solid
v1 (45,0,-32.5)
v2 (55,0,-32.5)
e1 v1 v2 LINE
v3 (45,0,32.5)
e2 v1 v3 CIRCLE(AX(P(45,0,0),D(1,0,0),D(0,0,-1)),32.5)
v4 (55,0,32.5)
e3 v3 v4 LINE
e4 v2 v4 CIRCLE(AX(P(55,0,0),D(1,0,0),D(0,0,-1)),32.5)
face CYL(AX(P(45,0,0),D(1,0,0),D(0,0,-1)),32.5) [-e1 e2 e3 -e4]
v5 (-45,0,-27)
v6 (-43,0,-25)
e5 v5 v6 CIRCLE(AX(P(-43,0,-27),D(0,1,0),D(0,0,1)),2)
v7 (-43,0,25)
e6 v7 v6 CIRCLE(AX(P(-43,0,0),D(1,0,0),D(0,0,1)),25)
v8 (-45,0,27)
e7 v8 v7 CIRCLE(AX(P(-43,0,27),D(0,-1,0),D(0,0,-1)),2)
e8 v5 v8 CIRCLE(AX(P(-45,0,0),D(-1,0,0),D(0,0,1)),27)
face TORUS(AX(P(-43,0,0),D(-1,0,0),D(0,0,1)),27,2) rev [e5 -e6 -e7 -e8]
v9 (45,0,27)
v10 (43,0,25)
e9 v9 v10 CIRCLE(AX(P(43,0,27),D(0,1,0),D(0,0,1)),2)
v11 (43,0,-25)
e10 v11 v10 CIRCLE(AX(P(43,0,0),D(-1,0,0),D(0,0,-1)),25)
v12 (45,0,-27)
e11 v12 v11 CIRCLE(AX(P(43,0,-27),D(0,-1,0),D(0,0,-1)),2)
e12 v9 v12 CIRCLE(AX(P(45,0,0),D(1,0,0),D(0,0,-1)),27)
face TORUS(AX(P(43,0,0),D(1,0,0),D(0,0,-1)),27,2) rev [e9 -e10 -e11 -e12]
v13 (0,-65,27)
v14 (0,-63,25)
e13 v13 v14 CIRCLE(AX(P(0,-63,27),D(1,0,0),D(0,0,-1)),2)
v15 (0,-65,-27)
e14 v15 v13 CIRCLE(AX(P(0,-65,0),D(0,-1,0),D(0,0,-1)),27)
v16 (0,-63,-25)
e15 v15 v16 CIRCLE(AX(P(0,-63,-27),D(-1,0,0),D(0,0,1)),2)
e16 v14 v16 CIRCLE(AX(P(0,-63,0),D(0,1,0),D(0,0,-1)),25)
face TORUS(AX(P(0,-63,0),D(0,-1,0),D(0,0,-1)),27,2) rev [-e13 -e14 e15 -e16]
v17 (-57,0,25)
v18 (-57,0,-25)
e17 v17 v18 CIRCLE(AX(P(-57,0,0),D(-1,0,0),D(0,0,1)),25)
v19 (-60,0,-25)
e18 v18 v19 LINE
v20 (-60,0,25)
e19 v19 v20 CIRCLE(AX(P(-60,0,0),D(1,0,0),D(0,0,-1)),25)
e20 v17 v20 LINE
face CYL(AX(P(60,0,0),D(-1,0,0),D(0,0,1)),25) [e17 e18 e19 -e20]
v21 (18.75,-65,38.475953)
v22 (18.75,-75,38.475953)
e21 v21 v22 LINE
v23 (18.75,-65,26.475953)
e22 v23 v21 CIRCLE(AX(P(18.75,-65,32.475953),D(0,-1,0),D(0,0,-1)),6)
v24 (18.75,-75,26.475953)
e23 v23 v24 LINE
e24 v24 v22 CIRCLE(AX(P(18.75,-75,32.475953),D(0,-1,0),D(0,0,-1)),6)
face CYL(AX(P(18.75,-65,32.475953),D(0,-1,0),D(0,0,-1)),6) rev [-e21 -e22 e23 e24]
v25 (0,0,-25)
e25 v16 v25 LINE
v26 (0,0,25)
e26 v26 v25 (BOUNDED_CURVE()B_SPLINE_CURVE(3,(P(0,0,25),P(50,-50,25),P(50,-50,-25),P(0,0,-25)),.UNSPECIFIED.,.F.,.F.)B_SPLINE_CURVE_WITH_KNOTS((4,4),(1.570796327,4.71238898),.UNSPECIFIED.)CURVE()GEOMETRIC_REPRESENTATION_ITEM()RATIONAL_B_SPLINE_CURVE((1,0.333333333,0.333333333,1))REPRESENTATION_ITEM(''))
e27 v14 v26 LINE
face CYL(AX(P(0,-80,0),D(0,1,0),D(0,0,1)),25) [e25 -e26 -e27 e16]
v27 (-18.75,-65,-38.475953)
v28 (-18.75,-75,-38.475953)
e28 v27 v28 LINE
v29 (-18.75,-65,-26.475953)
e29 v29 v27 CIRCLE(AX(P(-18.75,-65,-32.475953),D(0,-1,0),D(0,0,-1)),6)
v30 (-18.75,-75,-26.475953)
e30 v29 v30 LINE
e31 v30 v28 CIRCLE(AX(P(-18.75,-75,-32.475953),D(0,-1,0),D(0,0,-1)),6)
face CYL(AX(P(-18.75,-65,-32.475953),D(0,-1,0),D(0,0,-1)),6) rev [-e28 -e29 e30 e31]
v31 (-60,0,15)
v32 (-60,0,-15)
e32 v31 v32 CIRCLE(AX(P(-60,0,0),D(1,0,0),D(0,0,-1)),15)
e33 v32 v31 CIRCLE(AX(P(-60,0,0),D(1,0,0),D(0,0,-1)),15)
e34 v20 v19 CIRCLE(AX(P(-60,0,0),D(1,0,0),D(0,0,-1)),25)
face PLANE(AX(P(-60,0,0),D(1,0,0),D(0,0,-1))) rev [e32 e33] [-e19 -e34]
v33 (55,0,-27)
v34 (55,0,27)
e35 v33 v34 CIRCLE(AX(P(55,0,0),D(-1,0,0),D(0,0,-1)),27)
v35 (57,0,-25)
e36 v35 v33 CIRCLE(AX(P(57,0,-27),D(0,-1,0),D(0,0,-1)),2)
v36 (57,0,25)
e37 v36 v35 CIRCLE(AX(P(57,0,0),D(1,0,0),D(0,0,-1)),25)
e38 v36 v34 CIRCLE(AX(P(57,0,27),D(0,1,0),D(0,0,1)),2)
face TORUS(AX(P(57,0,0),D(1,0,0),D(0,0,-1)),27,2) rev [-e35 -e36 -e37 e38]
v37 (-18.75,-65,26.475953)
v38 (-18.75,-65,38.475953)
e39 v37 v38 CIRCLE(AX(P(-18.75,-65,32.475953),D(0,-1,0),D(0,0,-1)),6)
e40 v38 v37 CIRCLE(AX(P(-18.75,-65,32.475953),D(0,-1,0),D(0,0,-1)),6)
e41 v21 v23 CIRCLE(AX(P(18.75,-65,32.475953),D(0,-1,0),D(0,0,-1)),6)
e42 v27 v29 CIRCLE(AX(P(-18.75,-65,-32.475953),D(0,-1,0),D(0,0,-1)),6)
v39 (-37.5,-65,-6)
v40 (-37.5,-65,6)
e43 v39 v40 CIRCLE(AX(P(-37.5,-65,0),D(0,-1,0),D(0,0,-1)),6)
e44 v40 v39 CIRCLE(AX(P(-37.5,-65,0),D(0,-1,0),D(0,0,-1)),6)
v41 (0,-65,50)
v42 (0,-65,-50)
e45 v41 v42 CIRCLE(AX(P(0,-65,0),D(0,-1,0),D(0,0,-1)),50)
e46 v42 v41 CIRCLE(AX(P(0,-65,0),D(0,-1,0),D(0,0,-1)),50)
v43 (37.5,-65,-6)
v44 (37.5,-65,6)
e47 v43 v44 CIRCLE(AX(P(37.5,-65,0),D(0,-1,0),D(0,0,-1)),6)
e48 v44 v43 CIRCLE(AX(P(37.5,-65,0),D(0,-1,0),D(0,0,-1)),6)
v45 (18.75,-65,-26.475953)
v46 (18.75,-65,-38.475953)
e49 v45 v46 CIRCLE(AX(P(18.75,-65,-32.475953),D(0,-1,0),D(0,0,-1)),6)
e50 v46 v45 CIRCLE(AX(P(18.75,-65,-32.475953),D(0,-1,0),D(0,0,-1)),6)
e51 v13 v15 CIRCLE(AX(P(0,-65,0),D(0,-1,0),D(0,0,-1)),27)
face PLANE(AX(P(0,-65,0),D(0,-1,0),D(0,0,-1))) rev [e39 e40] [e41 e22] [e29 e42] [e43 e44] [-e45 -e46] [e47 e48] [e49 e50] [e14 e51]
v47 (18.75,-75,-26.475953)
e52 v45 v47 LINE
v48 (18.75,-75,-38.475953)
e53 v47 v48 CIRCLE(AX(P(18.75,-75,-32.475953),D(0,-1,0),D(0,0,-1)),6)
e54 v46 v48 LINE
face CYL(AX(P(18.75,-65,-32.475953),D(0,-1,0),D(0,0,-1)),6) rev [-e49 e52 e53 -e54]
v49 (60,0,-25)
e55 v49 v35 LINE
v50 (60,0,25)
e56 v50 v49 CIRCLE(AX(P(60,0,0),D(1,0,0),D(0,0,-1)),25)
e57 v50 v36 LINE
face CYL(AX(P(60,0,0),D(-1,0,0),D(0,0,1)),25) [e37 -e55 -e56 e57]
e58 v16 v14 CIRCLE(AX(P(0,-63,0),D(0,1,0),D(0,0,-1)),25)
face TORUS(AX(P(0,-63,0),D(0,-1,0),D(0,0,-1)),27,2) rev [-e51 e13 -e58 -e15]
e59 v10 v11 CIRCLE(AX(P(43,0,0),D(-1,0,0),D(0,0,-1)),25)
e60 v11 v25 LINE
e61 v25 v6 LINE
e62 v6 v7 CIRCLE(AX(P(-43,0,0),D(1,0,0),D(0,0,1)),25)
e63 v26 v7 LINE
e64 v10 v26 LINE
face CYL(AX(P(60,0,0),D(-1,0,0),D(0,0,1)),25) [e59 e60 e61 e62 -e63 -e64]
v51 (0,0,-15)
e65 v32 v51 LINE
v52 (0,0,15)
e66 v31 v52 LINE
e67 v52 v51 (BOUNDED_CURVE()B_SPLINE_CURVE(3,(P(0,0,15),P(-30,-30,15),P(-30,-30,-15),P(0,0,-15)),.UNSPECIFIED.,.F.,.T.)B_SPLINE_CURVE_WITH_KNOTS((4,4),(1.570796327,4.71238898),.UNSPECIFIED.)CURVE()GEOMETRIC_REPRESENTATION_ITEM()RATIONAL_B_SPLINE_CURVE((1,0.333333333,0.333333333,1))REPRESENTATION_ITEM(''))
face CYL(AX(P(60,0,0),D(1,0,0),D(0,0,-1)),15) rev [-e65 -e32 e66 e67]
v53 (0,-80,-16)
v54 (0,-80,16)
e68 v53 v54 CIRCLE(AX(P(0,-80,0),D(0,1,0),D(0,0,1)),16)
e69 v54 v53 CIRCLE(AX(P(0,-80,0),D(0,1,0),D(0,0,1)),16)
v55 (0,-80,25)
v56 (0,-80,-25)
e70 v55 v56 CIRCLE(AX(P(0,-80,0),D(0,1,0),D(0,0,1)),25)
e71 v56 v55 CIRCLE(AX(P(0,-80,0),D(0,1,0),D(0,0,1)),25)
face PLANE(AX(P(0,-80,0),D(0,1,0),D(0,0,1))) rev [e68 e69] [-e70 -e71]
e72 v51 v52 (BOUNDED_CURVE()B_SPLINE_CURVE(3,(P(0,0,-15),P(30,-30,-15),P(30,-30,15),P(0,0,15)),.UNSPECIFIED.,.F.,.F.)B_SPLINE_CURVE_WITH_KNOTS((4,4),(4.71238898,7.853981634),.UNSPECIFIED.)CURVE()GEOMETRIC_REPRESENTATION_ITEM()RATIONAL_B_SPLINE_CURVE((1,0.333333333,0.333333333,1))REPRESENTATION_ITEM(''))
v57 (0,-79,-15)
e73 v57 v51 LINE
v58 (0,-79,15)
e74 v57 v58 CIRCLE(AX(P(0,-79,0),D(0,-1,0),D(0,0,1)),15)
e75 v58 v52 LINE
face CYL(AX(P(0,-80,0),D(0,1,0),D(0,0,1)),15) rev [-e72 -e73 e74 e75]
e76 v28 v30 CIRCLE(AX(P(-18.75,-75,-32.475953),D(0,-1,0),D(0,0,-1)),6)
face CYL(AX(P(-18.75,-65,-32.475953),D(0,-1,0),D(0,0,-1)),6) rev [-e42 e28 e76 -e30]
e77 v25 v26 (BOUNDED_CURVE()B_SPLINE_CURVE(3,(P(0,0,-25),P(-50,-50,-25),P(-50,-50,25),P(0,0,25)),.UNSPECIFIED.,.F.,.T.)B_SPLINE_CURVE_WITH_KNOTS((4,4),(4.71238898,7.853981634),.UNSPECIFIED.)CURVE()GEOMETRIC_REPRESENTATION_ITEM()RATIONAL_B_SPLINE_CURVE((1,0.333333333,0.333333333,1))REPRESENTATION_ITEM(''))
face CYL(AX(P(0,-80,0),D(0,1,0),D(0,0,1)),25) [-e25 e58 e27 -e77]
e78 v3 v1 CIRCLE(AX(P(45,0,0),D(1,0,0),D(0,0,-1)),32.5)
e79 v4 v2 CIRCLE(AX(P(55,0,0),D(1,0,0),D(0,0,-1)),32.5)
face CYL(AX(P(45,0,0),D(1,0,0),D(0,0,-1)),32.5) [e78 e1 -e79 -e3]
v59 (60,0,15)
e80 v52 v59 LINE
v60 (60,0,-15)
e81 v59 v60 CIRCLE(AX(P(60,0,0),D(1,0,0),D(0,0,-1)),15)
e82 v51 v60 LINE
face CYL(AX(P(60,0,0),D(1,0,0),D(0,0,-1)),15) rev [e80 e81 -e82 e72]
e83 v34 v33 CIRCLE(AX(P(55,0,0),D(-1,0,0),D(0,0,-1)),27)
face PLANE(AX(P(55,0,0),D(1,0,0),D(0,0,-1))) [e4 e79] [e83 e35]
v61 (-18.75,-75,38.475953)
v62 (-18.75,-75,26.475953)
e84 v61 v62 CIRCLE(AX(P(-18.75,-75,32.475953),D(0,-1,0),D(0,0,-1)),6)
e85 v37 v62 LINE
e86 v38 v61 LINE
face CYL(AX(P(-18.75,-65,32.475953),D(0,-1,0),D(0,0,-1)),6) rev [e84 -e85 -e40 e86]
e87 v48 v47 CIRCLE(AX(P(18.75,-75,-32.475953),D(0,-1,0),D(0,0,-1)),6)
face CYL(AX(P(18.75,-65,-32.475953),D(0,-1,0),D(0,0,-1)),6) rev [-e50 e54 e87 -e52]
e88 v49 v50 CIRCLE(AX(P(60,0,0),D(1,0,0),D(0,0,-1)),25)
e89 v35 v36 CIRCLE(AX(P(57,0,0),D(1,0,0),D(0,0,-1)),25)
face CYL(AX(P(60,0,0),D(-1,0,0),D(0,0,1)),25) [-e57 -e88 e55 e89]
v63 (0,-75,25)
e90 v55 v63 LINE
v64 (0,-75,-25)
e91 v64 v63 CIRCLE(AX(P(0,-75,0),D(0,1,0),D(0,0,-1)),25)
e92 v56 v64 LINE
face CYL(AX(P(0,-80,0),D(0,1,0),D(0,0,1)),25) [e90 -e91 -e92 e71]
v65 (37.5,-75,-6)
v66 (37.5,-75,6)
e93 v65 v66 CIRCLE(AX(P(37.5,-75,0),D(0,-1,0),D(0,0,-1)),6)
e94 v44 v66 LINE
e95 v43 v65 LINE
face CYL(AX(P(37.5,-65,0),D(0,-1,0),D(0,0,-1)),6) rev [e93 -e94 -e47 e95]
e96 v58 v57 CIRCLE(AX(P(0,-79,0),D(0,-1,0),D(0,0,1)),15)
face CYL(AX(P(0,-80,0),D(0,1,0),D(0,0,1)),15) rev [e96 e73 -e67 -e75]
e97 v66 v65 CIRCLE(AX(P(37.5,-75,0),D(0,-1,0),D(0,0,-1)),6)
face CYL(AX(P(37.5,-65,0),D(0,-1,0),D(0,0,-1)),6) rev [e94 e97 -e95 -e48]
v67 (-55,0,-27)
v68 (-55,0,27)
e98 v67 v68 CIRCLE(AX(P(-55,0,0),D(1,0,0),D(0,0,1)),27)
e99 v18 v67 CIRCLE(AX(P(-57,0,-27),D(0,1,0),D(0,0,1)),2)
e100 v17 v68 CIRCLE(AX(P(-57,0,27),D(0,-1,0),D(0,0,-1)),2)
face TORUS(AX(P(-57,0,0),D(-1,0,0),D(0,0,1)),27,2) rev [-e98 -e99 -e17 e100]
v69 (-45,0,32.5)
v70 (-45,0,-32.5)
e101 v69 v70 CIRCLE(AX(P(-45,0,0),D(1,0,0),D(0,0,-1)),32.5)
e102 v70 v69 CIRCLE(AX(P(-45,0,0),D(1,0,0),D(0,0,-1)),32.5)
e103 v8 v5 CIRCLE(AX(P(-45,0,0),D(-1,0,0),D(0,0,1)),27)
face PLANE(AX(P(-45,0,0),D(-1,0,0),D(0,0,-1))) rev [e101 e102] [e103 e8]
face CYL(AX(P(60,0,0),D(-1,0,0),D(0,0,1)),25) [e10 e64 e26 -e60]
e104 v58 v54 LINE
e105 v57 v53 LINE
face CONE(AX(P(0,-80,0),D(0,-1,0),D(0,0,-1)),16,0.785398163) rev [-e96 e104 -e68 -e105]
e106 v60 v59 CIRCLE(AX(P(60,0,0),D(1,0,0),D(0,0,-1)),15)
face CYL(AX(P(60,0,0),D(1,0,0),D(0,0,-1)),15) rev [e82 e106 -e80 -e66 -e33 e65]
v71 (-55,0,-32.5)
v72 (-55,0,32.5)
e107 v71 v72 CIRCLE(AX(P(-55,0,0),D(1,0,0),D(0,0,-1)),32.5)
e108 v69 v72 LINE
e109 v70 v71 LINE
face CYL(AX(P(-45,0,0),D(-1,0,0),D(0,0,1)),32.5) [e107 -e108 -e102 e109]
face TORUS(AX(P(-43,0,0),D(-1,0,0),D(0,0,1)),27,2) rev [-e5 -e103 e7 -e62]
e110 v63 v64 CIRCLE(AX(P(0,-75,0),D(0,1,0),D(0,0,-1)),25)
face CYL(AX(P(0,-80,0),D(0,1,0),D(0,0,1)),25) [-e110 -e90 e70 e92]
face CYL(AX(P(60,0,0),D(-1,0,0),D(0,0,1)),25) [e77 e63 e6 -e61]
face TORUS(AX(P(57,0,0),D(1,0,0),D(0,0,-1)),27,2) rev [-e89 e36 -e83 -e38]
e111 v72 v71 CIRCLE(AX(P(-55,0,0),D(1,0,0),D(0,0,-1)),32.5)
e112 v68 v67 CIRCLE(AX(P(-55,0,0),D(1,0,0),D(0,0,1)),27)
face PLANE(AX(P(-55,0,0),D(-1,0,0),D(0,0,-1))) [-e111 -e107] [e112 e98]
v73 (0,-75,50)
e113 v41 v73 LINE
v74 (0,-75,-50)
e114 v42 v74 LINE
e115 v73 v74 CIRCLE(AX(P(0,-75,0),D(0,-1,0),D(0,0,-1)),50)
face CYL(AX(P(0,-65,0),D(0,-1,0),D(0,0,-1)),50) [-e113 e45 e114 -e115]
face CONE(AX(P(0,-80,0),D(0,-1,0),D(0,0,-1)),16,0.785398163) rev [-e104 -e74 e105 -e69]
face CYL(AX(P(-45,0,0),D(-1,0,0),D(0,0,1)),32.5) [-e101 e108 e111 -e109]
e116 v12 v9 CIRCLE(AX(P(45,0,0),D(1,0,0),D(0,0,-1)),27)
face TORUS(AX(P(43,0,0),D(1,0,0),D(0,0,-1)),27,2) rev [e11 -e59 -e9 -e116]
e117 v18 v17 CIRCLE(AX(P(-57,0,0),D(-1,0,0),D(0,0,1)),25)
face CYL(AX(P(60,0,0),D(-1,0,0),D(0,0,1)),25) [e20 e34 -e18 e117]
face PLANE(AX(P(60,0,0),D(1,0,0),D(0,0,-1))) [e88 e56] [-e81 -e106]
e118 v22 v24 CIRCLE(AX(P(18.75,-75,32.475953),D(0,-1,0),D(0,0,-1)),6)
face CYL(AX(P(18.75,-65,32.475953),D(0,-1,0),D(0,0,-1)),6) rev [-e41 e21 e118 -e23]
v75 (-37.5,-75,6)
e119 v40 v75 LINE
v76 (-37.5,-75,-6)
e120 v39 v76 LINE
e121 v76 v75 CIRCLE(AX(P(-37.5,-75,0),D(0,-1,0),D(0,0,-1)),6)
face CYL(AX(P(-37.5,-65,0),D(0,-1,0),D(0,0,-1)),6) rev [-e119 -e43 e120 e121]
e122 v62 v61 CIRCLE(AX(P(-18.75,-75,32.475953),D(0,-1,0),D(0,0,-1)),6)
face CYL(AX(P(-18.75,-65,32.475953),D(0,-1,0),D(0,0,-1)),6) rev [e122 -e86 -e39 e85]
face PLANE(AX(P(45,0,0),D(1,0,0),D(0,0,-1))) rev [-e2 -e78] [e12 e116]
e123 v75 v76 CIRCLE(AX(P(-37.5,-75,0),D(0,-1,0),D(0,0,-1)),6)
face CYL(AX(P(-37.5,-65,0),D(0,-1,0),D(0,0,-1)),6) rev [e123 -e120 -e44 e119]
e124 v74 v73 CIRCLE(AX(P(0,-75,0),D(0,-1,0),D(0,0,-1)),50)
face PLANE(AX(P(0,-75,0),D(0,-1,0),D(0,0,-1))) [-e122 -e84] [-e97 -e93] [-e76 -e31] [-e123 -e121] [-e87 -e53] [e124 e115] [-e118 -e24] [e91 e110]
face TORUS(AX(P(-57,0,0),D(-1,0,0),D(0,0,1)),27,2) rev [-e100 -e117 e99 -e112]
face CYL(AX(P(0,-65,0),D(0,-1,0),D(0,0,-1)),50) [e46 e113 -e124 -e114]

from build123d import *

# Parameters (mm, degrees)
MAIN_PIPE_SKETCH_R             = 25
MAIN_PIPE_50X120_DEPTH         = 60
END_START                      = -5
END_COLLAR_SKETCH_R            = 32.5
END_COLLAR_SKETCH_R_2          = 25
END_COLLAR_65_DEPTH            = 10
BRANCH_PIPE_SKETCH_R           = 25
BRANCH_PIPE_SKETCH_R_2         = 15
BRANCH_PIPE_50_DEPTH           = 80
MAIN_BORE_30_THRU_D            = 30
BRANCH_BORE_SKETCH_R           = 15
BRANCH_BORE_CUT_DEPTH          = 80
BASE_START                     = -15
BASE_FLANGE_SKETCH_R           = 50
BASE_FLANGE_SKETCH_R_2         = 6
BASE_FLANGE_SKETCH_R_3         = 25
BASE_FLANGE_100_6X_12_DEPTH    = 10
COLLAR_AND_FLANGE_FILLETS_R2_R = 2
BRANCH_EDGE_CHAMFER_1MM_SIZE   = 1


with BuildPart() as part:
    # Main Pipe Sketch → Main Pipe Ø50x120 (new, symmetric)
    with BuildSketch(Plane(origin=(0, 0, 0), x_dir=(0, 0, -1), z_dir=(1, 0, 0))):
        Circle(MAIN_PIPE_SKETCH_R)
    extrude(amount=MAIN_PIPE_50X120_DEPTH, both=True)

    # End Collar Sketch → End Collar Ø65 (add)
    with BuildSketch(Plane(origin=(60, 0, 0), x_dir=(0, 0, -1), z_dir=(1, 0, 0)).offset(END_START)):
        Circle(END_COLLAR_SKETCH_R)
        Circle(END_COLLAR_SKETCH_R_2, mode=Mode.SUBTRACT)
    end_collar_65 = extrude(amount=-END_COLLAR_65_DEPTH)

    # End Collar Mirror: End Collar Ø65 across plane
    add(end_collar_65.mirror(Plane(origin=(0, 0, 0), x_dir=(0, 0, 1), z_dir=(1, 0, 0))))

    # Branch Pipe Sketch → Branch Pipe Ø50 (add)
    with BuildSketch(Plane(origin=(0, 0, 0), x_dir=(1, 0, 0), z_dir=(0, 1, 0))):
        with Locations(Location((0, 0, 0), (0, 0, 270))):
            Circle(BRANCH_PIPE_SKETCH_R)
        with Locations(Location((0, 0, 0), (0, 0, 270))):
            Circle(BRANCH_PIPE_SKETCH_R_2, mode=Mode.SUBTRACT)
    extrude(amount=-BRANCH_PIPE_50_DEPTH)

    # Main Bore Ø30 Thru (through all)
    with Locations(Plane(origin=(60, 0, 0), x_dir=(0, 0, -1), z_dir=(1, 0, 0))):
        with Locations((0, 0)):
            Hole(MAIN_BORE_30_THRU_D / 2)

    # Branch Bore Sketch → Branch Bore Cut (cut)
    with BuildSketch(Plane(origin=(0, 0, 0), x_dir=(1, 0, 0), z_dir=(0, 1, 0))):
        with Locations(Location((0, 0, 0), (0, 0, 270))):
            Circle(BRANCH_BORE_SKETCH_R)
    extrude(amount=-BRANCH_BORE_CUT_DEPTH, mode=Mode.SUBTRACT)

    # Base Flange Sketch → Base Flange Ø100 6xØ12 (add)
    with BuildSketch(Plane.XZ.offset(80).offset(BASE_START)):
        with Locations(Location((0, 0, 0), (0, 0, 270))):
            Circle(BASE_FLANGE_SKETCH_R)
        with Locations(Location((37.5, 0, 0), (0, 0, 270))):
            Circle(BASE_FLANGE_SKETCH_R_2, mode=Mode.SUBTRACT)
        with Locations(Location((0, 0, 0), (0, 0, 270))):
            Circle(BASE_FLANGE_SKETCH_R_3, mode=Mode.SUBTRACT)
        with Locations(Location((18.75, -32.475952642, 0), (0, 0, 270))):
            Circle(BASE_FLANGE_SKETCH_R_2, mode=Mode.SUBTRACT)
        with Locations(Location((-18.75, -32.475952642, 0), (0, 0, 270))):
            Circle(BASE_FLANGE_SKETCH_R_2, mode=Mode.SUBTRACT)
        with Locations(Location((-37.5, 0, 0), (0, 0, 270))):
            Circle(BASE_FLANGE_SKETCH_R_2, mode=Mode.SUBTRACT)
        with Locations(Location((-18.75, 32.475952642, 0), (0, 0, 270))):
            Circle(BASE_FLANGE_SKETCH_R_2, mode=Mode.SUBTRACT)
        with Locations(Location((18.75, 32.475952642, 0), (0, 0, 270))):
            Circle(BASE_FLANGE_SKETCH_R_2, mode=Mode.SUBTRACT)
    extrude(amount=BASE_FLANGE_100_6X_12_DEPTH)

    # Collar and Flange Fillets R2
    collar_and_flange_fillets_r2_edges = [part.edges().sort_by_distance(p)[0] for p in [
        (-45, 0, 25),
        (-55, 0, 25),
        (0, -65, -25),
        (45, 0, 25),
        (55, 0, 25),
    ]]
    fillet(collar_and_flange_fillets_r2_edges, radius=COLLAR_AND_FLANGE_FILLETS_R2_R)

    # Branch Edge Chamfer 1mm
    branch_edge_chamfer_1mm_edges = [part.edges().sort_by_distance(p)[0] for p in [
        (0, -80, -15),
    ]]
    chamfer(branch_edge_chamfer_1mm_edges, length=BRANCH_EDGE_CHAMFER_1MM_SIZE)


solid = part.part
